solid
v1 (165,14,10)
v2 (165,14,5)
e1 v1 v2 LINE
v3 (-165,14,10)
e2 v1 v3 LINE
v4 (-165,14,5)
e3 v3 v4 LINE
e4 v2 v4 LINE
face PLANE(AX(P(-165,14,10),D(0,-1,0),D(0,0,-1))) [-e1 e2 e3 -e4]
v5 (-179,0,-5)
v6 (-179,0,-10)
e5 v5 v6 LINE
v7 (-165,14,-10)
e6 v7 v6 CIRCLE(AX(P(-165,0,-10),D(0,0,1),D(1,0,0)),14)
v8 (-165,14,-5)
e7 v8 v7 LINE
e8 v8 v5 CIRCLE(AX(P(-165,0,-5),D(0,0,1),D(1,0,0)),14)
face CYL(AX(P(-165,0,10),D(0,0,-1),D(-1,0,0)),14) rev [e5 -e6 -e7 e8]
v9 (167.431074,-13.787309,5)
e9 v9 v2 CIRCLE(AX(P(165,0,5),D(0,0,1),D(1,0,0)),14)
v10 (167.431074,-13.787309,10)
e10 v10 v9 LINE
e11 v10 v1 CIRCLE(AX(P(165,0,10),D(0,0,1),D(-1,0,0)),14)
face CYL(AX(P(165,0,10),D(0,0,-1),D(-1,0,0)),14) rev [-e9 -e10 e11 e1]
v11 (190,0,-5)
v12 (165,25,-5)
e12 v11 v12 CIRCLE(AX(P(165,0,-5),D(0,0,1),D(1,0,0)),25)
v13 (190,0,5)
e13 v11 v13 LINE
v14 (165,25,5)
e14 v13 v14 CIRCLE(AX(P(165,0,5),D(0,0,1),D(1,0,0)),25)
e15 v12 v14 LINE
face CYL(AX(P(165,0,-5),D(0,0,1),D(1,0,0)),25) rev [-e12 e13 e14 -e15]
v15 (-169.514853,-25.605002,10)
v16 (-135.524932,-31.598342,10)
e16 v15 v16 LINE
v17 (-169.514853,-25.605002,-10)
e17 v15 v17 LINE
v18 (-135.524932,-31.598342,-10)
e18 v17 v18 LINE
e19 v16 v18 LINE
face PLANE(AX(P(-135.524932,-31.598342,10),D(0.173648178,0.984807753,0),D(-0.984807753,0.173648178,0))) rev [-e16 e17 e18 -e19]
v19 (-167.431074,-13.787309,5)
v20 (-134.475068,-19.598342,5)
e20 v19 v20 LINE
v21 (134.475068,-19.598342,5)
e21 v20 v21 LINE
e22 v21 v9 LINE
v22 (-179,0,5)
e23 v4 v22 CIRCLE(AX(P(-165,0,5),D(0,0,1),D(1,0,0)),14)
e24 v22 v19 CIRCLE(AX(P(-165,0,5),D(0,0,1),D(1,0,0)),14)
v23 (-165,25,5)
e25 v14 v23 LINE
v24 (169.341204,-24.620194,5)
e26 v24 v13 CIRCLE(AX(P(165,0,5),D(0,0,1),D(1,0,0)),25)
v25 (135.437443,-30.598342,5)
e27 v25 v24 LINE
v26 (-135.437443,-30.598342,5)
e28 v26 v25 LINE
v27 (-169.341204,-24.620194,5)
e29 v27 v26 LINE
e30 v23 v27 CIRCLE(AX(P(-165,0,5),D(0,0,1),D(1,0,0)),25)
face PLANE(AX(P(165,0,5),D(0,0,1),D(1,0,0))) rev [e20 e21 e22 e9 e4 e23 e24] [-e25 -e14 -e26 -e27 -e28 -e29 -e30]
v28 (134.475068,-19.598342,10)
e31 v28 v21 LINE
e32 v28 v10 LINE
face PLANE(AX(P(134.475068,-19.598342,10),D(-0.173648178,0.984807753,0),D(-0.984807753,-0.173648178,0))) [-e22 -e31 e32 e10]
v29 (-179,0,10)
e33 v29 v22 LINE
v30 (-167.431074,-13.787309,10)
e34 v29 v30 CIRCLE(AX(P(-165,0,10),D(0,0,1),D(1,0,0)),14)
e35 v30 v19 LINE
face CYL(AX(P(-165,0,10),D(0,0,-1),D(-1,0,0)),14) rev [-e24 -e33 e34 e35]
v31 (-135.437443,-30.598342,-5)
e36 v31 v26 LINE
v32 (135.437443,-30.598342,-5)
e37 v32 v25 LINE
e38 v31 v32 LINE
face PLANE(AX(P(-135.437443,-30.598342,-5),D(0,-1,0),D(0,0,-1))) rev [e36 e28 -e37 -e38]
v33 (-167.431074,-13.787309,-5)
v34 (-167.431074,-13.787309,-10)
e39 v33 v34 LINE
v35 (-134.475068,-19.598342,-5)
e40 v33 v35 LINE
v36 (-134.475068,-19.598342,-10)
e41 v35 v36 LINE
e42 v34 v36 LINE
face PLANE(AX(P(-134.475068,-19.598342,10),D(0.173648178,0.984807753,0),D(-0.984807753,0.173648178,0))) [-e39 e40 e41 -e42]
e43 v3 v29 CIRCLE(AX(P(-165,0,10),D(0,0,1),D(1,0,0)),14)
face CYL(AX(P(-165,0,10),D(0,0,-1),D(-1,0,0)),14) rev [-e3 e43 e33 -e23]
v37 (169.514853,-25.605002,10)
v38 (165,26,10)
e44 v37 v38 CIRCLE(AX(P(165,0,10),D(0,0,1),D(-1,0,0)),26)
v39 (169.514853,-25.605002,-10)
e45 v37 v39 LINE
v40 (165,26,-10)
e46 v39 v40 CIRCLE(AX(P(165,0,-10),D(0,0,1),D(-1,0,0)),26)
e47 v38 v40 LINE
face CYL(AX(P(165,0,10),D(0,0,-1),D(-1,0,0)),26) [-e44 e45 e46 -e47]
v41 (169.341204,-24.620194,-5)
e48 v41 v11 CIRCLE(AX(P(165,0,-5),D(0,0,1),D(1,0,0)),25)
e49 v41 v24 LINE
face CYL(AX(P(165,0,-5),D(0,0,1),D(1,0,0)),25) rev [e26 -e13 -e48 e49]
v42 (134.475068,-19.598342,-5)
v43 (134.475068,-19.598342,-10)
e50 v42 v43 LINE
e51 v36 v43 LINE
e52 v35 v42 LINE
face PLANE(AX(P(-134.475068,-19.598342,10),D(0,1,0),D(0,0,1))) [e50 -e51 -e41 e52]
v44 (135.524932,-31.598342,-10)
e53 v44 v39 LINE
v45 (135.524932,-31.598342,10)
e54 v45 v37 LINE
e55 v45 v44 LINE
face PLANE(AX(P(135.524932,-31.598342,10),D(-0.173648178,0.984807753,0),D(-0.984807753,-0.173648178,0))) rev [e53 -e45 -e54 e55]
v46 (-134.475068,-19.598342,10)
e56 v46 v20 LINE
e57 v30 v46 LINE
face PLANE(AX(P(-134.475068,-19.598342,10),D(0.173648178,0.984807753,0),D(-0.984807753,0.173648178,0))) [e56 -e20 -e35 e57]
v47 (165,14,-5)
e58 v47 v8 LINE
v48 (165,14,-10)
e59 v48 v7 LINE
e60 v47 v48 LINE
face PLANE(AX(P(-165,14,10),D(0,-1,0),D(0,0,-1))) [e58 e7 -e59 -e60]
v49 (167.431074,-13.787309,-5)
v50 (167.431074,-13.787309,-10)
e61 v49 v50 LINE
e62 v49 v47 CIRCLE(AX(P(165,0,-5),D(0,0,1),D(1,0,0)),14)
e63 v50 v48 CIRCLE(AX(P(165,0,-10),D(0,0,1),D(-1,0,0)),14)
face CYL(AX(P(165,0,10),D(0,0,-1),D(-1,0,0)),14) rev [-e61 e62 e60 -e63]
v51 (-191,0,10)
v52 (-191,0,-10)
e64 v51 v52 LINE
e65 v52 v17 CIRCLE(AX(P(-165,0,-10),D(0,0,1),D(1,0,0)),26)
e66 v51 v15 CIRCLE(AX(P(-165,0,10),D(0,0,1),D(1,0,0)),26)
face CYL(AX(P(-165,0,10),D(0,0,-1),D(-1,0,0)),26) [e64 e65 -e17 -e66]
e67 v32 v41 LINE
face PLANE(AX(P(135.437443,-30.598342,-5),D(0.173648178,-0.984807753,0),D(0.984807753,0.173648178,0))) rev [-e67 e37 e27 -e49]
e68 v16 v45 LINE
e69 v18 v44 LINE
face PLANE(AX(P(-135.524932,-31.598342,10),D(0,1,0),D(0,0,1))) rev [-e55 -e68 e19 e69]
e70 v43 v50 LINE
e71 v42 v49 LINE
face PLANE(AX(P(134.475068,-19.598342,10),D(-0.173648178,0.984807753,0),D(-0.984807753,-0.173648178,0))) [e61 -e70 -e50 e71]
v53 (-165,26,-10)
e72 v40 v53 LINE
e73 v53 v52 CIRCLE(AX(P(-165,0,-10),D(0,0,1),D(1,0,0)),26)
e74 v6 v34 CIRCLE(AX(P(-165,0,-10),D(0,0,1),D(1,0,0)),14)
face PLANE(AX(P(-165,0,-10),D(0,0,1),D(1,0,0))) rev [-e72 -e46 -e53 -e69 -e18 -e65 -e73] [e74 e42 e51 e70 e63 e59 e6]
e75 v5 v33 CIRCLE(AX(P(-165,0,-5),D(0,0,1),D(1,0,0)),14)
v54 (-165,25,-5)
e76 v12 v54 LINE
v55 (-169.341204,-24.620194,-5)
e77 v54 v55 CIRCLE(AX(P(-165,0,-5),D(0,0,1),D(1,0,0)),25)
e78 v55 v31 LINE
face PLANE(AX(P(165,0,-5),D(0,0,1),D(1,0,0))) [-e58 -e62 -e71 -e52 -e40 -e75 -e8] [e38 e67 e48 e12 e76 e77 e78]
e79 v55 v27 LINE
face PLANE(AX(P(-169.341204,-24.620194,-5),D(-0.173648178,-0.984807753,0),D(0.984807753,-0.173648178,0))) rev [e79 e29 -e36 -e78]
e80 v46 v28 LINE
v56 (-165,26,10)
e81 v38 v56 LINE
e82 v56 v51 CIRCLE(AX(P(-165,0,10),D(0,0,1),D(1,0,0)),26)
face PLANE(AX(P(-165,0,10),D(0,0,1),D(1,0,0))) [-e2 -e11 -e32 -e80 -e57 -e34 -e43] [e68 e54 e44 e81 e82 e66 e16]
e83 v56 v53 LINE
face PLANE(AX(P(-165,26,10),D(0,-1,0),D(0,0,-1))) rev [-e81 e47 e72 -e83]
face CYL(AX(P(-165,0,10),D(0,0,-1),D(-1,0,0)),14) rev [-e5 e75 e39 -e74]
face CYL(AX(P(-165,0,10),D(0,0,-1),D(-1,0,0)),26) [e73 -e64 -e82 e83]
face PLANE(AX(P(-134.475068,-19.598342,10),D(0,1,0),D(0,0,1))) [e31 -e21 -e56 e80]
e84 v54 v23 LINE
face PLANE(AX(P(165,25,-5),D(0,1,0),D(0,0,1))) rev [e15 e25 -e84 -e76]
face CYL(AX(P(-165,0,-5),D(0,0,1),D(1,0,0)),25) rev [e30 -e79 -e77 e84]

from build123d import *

# Parameters (mm, degrees)
BOSS_EXTRUDE1_DEPTH = 10
CUT_EXTRUDE1_DEPTH  = 5


with BuildPart() as part:
    # Sketch2 → Boss-Extrude1 (new, symmetric)
    with BuildSketch(Plane.XY):
        with BuildLine():
            Line((-165, 26), (165, 26))
            ThreePointArc((165, 26), (190.90106215, 2.266049311), (169.514852619, -25.605001578))
            Line((169.514852619, -25.605001578), (135.524931981, -31.598341659))
            Line((135.524931981, -31.598341659), (-135.524931981, -31.598341659))
            Line((-135.524931981, -31.598341659), (-169.514852619, -25.605001578))
            ThreePointArc((-169.514852619, -25.605001578), (-190.90106215, 2.266049311), (-165, 26))
        make_face()
        with BuildLine():
            Line((-165, 14), (165, 14))
            ThreePointArc((165, 14), (178.946725773, 1.220180398), (167.431074487, -13.787308542))
            Line((167.431074487, -13.787308542), (134.475068019, -19.598341659))
            Line((134.475068019, -19.598341659), (-134.475068019, -19.598341659))
            Line((-134.475068019, -19.598341659), (-167.431074487, -13.787308542))
            ThreePointArc((-167.431074487, -13.787308542), (-178.946725773, 1.220180398), (-165, 14))
        make_face(mode=Mode.SUBTRACT)
    extrude(amount=BOSS_EXTRUDE1_DEPTH, both=True)

    # Sketch8 → Cut-Extrude1 (cut, symmetric)
    with BuildSketch(Plane.XY):
        with BuildLine():
            Line((135.437443318, -30.598341659), (169.341204442, -24.620193825))
            ThreePointArc((169.341204442, -24.620193825), (189.904867452, 2.178893569), (165, 25))
            Line((165, 25), (-165, 25))
            ThreePointArc((-165, 25), (-189.904867452, 2.178893569), (-169.341204442, -24.620193825))
            Line((-169.341204442, -24.620193825), (-135.437443318, -30.598341659))
            Line((-135.437443318, -30.598341659), (135.437443318, -30.598341659))
        make_face()
    extrude(amount=CUT_EXTRUDE1_DEPTH, both=True, mode=Mode.SUBTRACT)


solid = part.part
